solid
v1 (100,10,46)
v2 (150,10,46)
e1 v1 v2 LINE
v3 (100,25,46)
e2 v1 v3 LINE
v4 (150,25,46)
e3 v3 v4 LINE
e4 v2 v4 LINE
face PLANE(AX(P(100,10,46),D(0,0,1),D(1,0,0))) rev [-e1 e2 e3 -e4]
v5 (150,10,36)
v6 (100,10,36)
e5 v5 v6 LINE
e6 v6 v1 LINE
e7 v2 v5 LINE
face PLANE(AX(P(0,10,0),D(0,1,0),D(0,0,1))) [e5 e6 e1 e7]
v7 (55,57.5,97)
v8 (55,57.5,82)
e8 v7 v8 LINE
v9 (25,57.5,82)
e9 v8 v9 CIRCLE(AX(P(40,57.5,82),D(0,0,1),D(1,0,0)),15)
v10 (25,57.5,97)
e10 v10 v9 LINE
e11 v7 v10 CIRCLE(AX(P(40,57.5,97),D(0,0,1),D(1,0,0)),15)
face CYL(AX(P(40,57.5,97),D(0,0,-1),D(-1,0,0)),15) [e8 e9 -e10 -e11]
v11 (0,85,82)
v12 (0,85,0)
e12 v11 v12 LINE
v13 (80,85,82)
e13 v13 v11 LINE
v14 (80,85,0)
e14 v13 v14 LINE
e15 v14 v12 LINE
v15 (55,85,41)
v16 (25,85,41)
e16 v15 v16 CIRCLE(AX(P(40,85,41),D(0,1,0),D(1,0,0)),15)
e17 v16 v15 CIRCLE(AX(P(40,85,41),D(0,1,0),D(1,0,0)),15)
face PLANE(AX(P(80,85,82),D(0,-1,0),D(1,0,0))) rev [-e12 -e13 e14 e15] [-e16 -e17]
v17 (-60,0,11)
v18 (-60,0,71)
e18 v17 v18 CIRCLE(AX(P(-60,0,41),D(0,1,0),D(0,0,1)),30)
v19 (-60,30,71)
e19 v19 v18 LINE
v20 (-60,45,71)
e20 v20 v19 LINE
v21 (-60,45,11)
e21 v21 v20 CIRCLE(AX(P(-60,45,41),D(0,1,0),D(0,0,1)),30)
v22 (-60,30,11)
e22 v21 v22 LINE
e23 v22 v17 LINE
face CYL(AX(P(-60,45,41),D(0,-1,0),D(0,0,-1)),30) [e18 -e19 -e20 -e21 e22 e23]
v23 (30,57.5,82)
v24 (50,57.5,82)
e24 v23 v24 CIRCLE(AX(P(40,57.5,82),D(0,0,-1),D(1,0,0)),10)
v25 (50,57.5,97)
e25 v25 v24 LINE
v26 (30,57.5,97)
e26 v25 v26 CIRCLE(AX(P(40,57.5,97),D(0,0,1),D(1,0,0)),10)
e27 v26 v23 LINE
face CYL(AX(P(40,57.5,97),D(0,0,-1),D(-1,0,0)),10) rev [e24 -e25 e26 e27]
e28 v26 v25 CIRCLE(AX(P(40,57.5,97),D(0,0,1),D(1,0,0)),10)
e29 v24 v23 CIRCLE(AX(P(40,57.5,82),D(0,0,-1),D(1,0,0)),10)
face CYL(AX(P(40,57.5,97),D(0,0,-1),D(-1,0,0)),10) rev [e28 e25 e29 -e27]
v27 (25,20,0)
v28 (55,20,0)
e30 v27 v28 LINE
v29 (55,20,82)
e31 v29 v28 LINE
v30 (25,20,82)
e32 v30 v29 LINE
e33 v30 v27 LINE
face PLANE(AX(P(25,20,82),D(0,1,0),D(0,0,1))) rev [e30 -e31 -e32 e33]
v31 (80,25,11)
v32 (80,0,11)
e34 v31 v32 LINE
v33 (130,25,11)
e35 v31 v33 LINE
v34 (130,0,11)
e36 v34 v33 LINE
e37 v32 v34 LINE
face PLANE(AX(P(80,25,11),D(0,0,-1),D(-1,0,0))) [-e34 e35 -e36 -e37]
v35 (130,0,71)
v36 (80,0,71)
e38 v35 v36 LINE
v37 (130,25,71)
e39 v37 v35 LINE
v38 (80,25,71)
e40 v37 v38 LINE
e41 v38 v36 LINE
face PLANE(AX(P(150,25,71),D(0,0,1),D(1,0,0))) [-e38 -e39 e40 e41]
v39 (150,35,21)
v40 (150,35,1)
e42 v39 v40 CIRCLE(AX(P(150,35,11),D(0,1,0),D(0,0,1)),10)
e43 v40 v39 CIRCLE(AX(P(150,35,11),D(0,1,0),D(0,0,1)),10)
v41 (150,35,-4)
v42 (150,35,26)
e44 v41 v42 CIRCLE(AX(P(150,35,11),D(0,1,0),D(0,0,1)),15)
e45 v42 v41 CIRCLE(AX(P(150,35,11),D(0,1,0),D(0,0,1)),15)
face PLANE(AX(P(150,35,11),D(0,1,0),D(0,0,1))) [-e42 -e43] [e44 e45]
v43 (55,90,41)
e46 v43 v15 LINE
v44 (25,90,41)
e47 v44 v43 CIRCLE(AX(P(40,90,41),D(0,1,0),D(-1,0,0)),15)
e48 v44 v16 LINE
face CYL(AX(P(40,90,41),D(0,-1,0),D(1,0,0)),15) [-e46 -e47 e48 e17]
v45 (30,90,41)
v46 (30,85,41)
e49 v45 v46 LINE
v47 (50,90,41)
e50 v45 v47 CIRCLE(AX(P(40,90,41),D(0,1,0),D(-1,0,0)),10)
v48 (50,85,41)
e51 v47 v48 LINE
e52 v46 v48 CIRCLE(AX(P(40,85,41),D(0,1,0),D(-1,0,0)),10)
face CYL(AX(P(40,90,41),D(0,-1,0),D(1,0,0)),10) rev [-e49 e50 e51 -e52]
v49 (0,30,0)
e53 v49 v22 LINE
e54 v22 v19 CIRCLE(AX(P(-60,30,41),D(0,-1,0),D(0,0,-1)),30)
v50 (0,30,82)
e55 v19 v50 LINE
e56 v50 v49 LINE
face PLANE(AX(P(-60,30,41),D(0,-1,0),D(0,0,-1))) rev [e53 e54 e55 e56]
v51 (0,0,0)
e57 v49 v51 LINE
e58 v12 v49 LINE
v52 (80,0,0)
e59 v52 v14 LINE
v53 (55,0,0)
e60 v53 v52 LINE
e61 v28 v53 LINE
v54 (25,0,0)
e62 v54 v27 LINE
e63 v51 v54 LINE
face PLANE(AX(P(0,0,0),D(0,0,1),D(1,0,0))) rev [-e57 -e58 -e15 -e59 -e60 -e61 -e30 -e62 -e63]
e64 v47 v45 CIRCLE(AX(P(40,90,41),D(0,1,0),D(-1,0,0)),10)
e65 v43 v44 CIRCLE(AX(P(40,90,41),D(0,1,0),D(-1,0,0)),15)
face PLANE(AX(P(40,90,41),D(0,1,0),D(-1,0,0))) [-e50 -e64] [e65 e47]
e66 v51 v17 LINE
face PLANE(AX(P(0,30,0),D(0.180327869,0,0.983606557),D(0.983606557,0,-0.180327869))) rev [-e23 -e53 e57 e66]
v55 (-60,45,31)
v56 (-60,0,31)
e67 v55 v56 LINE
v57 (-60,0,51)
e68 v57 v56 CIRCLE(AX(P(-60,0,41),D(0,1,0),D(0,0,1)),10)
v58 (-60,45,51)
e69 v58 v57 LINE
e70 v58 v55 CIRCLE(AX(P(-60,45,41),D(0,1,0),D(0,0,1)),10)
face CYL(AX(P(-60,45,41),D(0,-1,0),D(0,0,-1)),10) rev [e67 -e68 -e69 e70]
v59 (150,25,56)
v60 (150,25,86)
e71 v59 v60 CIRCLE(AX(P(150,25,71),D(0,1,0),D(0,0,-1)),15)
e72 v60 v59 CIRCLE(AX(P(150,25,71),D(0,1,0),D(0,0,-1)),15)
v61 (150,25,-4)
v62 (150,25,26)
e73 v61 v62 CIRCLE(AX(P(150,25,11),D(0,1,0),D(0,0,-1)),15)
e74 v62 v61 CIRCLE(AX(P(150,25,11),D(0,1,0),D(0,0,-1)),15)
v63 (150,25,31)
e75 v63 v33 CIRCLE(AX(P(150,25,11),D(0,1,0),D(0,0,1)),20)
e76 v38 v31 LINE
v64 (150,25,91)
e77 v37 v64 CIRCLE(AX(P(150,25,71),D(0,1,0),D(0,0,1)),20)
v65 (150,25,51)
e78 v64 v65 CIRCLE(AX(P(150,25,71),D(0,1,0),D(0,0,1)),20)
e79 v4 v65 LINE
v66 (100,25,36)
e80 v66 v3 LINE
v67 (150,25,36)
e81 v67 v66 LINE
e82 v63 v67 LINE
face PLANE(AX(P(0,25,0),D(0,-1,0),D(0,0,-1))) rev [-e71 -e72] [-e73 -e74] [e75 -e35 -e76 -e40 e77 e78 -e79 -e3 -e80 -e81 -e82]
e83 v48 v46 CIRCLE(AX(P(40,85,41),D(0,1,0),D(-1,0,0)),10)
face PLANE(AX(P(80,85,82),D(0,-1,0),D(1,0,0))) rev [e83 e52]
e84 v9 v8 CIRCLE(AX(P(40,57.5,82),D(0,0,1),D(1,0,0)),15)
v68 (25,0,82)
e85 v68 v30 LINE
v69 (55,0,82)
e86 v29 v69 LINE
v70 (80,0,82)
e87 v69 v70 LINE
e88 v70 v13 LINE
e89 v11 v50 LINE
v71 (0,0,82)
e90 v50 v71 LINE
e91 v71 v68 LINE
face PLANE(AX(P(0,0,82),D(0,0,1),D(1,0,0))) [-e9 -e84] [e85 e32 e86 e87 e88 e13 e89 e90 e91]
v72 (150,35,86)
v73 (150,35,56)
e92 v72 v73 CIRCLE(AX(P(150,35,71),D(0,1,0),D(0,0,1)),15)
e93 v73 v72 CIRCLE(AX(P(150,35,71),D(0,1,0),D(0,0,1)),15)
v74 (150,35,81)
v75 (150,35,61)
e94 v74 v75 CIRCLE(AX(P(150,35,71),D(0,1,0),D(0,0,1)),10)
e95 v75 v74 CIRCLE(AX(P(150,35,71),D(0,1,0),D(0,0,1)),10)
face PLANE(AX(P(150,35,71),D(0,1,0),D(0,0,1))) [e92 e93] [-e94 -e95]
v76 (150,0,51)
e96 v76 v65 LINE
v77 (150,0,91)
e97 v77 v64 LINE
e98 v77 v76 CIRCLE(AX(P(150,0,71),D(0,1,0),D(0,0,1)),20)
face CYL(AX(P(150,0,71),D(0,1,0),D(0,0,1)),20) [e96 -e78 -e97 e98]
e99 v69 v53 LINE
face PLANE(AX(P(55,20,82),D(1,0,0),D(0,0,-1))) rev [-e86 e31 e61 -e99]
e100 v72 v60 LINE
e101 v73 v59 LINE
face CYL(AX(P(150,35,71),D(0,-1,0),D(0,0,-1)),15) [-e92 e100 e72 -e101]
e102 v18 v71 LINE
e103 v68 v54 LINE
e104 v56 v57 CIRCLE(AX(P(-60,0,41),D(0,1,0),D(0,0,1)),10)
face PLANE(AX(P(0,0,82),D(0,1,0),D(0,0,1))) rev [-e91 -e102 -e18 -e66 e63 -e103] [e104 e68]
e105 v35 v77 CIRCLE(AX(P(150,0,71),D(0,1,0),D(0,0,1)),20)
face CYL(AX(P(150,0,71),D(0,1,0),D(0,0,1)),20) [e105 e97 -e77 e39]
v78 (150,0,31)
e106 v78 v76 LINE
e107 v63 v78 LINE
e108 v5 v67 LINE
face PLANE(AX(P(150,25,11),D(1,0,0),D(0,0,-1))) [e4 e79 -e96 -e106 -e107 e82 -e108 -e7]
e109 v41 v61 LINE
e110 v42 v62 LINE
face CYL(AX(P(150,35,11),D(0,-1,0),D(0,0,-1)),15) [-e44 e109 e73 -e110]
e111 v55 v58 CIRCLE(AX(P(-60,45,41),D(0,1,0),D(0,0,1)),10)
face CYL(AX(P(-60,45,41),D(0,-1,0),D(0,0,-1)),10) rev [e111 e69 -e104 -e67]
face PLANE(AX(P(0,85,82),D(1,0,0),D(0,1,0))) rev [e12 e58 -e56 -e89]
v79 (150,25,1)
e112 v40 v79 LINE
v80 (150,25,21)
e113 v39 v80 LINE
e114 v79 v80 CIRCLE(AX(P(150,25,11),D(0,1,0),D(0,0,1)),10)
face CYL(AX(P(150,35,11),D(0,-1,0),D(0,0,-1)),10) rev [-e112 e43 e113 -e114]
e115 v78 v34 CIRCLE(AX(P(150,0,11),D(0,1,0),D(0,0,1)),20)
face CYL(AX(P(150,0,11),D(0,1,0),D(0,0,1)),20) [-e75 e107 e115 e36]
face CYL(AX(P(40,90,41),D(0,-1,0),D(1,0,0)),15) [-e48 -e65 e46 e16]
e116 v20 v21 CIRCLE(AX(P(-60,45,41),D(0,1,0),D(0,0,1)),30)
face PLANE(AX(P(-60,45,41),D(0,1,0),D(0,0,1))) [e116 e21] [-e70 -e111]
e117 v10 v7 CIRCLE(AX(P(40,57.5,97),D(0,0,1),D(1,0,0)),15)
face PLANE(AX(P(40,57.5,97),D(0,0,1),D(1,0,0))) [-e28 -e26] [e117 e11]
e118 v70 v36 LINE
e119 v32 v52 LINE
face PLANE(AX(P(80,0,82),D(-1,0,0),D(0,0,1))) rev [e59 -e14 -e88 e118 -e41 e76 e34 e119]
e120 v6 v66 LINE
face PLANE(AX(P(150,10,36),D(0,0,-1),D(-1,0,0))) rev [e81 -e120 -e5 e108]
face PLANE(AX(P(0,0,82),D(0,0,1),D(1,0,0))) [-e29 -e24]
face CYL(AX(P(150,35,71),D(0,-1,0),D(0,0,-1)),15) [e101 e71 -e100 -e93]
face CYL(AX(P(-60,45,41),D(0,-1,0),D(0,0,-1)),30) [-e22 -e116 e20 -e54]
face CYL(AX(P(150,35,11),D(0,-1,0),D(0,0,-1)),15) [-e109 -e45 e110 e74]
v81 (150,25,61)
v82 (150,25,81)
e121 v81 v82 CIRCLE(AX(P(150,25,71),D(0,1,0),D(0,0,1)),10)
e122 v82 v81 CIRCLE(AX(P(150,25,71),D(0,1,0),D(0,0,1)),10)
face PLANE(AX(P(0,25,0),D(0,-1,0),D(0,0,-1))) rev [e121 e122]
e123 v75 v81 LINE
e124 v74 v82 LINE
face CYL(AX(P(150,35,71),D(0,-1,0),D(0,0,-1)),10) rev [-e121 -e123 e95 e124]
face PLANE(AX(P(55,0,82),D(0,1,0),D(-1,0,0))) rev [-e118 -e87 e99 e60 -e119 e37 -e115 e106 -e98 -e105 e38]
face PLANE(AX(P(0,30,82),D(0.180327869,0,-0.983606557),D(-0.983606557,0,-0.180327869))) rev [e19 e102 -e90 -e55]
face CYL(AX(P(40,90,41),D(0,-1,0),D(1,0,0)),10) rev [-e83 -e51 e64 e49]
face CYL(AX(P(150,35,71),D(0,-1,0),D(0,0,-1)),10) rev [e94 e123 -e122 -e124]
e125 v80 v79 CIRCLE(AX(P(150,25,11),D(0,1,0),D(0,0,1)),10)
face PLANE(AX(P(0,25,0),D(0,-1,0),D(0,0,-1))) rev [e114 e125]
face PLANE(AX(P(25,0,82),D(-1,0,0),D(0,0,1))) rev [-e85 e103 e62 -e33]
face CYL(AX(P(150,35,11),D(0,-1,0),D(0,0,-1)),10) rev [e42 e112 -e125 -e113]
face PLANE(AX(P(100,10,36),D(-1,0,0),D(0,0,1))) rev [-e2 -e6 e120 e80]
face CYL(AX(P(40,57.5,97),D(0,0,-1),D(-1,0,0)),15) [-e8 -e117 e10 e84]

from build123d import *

# Parameters (mm, degrees)
MAIN_BLOCK_DEPTH          = 82
SIDE_LUG_PROFILE_R        = 30
SIDE_LUG_PROFILE_R_2      = 10
SIDE_LUG_BOSS_DEPTH       = 45
GUSSET_BOSS_DEPTH         = 30
MOUNTING_TAB_PROFILE_W    = 70
MOUNTING_TAB_PROFILE_H    = 60
MOUNTING_TAB_DEPTH        = 25
TAB_EYE_PROFILE_R         = 20
TAB_EYE_BOSS_DEPTH        = 25
TAB_RING_PROFILES_R       = 15
TAB_RING_PROFILES_R_2     = 10
TAB_BOSS_RINGS_DEPTH      = 10
SIDE_HUB_RING_PROFILE_R   = 15
SIDE_HUB_RING_PROFILE_R_2 = 10
SIDE_HUB_RING_DEPTH       = 5
TOP_HUB_RING_PROFILE_R    = 15
TOP_HUB_RING_PROFILE_R_2  = 10
TOP_HUB_RING_DEPTH        = 15
TAB_SLOT_CUT_DEPTH        = 15


with BuildPart() as part:
    # Main Block Profile → Main Block (new body)
    with BuildSketch(Plane.XY):
        Polygon((0, 0), (25, 0), (25, 20), (55, 20), (55, 0), (80, 0), (80, 85), (0, 85), align=None)
    extrude(amount=MAIN_BLOCK_DEPTH)



with BuildPart() as body_2:
    # Side Lug Profile → Side Lug Boss (new body)
    with BuildSketch(Plane(origin=(0, 0, 0), x_dir=(1, 0, 0), z_dir=(0, 1, 0))):
        with Locations(Location((-60, -41, 0), (0, 0, 90))):
            Circle(SIDE_LUG_PROFILE_R)
        with Locations(Location((-60, -41, 0), (0, 0, 90))):
            Circle(SIDE_LUG_PROFILE_R_2, mode=Mode.SUBTRACT)
    extrude(amount=SIDE_LUG_BOSS_DEPTH)


with BuildPart() as part_1:
    add(part.part)

    add(body_2.part)  # Gusset Boss merges body 2
    # Gusset Profile → Gusset Boss (add)
    with BuildSketch(Plane(origin=(0, 0, 0), x_dir=(1, 0, 0), z_dir=(0, 1, 0))):
        with BuildLine():
            Line((0, 0), (-60, -11))
            ThreePointArc((-60, -11), (-30, -41), (-60, -71))
            Line((-60, -71), (0, -82))
            Line((0, -82), (0, 0))
        make_face()
    extrude(amount=GUSSET_BOSS_DEPTH)

    # Mounting Tab Profile → Mounting Tab (add)
    with BuildSketch(Plane(origin=(0, 0, 0), x_dir=(1, 0, 0), z_dir=(0, 1, 0))):
        with Locations((115, -41)):
            Rectangle(MOUNTING_TAB_PROFILE_W, MOUNTING_TAB_PROFILE_H)
    extrude(amount=MOUNTING_TAB_DEPTH)

    # Tab Eye Profile → Tab Eye Boss (add)
    with BuildSketch(Plane(origin=(0, 25, 0), x_dir=(1, 0, 0), z_dir=(0, 1, 0))):
        with Locations((150, -11)):
            Circle(TAB_EYE_PROFILE_R)
        with Locations((150, -71)):
            Circle(TAB_EYE_PROFILE_R)
    extrude(amount=-TAB_EYE_BOSS_DEPTH)

    # Tab Ring Profiles → Tab Boss Rings (add)
    # profile 1 of 2: a face of its own
    with BuildSketch(Plane(origin=(0, 25, 0), x_dir=(1, 0, 0), z_dir=(0, 1, 0))):
        with Locations(Location((150, -11, 0), (0, 0, 90))):
            Circle(TAB_RING_PROFILES_R)
        with Locations(Location((150, -11, 0), (0, 0, 270))):
            Circle(TAB_RING_PROFILES_R_2, mode=Mode.SUBTRACT)
    # profile 2 of 2: a face of its own
    with BuildSketch(Plane(origin=(0, 25, 0), x_dir=(1, 0, 0), z_dir=(0, 1, 0))):
        with Locations(Location((150, -71, 0), (0, 0, 90))):
            Circle(TAB_RING_PROFILES_R)
        with Locations(Location((150, -71, 0), (0, 0, 270))):
            Circle(TAB_RING_PROFILES_R_2, mode=Mode.SUBTRACT)
    extrude(amount=TAB_BOSS_RINGS_DEPTH)

    # Side Hub Ring Profile → Side Hub Ring (add)
    with BuildSketch(Plane(origin=(0, 85, 0), x_dir=(1, 0, 0), z_dir=(0, 1, 0))):
        with Locations((40, -41)):
            Circle(SIDE_HUB_RING_PROFILE_R)
        with Locations(Location((40, -41, 0), (0, 0, 180))):
            Circle(SIDE_HUB_RING_PROFILE_R_2, mode=Mode.SUBTRACT)
    extrude(amount=SIDE_HUB_RING_DEPTH)

    # Top Hub Ring Profile → Top Hub Ring (add)
    with BuildSketch(Plane.XY.offset(82)):
        with Locations((40, 57.5)):
            Circle(TOP_HUB_RING_PROFILE_R)
        with Locations((40, 57.5)):
            Circle(TOP_HUB_RING_PROFILE_R_2, mode=Mode.SUBTRACT)
    extrude(amount=TOP_HUB_RING_DEPTH)

    # Tab Slot Profile → Tab Slot Cut (cut)
    with BuildSketch(Plane(origin=(0, 25, 0), x_dir=(1, 0, 0), z_dir=(0, 1, 0))):
        Polygon((150, -41), (150, -36), (100, -36), (100, -46), (150, -46), align=None)
    extrude(amount=-TAB_SLOT_CUT_DEPTH, mode=Mode.SUBTRACT)


solid = part_1.part
